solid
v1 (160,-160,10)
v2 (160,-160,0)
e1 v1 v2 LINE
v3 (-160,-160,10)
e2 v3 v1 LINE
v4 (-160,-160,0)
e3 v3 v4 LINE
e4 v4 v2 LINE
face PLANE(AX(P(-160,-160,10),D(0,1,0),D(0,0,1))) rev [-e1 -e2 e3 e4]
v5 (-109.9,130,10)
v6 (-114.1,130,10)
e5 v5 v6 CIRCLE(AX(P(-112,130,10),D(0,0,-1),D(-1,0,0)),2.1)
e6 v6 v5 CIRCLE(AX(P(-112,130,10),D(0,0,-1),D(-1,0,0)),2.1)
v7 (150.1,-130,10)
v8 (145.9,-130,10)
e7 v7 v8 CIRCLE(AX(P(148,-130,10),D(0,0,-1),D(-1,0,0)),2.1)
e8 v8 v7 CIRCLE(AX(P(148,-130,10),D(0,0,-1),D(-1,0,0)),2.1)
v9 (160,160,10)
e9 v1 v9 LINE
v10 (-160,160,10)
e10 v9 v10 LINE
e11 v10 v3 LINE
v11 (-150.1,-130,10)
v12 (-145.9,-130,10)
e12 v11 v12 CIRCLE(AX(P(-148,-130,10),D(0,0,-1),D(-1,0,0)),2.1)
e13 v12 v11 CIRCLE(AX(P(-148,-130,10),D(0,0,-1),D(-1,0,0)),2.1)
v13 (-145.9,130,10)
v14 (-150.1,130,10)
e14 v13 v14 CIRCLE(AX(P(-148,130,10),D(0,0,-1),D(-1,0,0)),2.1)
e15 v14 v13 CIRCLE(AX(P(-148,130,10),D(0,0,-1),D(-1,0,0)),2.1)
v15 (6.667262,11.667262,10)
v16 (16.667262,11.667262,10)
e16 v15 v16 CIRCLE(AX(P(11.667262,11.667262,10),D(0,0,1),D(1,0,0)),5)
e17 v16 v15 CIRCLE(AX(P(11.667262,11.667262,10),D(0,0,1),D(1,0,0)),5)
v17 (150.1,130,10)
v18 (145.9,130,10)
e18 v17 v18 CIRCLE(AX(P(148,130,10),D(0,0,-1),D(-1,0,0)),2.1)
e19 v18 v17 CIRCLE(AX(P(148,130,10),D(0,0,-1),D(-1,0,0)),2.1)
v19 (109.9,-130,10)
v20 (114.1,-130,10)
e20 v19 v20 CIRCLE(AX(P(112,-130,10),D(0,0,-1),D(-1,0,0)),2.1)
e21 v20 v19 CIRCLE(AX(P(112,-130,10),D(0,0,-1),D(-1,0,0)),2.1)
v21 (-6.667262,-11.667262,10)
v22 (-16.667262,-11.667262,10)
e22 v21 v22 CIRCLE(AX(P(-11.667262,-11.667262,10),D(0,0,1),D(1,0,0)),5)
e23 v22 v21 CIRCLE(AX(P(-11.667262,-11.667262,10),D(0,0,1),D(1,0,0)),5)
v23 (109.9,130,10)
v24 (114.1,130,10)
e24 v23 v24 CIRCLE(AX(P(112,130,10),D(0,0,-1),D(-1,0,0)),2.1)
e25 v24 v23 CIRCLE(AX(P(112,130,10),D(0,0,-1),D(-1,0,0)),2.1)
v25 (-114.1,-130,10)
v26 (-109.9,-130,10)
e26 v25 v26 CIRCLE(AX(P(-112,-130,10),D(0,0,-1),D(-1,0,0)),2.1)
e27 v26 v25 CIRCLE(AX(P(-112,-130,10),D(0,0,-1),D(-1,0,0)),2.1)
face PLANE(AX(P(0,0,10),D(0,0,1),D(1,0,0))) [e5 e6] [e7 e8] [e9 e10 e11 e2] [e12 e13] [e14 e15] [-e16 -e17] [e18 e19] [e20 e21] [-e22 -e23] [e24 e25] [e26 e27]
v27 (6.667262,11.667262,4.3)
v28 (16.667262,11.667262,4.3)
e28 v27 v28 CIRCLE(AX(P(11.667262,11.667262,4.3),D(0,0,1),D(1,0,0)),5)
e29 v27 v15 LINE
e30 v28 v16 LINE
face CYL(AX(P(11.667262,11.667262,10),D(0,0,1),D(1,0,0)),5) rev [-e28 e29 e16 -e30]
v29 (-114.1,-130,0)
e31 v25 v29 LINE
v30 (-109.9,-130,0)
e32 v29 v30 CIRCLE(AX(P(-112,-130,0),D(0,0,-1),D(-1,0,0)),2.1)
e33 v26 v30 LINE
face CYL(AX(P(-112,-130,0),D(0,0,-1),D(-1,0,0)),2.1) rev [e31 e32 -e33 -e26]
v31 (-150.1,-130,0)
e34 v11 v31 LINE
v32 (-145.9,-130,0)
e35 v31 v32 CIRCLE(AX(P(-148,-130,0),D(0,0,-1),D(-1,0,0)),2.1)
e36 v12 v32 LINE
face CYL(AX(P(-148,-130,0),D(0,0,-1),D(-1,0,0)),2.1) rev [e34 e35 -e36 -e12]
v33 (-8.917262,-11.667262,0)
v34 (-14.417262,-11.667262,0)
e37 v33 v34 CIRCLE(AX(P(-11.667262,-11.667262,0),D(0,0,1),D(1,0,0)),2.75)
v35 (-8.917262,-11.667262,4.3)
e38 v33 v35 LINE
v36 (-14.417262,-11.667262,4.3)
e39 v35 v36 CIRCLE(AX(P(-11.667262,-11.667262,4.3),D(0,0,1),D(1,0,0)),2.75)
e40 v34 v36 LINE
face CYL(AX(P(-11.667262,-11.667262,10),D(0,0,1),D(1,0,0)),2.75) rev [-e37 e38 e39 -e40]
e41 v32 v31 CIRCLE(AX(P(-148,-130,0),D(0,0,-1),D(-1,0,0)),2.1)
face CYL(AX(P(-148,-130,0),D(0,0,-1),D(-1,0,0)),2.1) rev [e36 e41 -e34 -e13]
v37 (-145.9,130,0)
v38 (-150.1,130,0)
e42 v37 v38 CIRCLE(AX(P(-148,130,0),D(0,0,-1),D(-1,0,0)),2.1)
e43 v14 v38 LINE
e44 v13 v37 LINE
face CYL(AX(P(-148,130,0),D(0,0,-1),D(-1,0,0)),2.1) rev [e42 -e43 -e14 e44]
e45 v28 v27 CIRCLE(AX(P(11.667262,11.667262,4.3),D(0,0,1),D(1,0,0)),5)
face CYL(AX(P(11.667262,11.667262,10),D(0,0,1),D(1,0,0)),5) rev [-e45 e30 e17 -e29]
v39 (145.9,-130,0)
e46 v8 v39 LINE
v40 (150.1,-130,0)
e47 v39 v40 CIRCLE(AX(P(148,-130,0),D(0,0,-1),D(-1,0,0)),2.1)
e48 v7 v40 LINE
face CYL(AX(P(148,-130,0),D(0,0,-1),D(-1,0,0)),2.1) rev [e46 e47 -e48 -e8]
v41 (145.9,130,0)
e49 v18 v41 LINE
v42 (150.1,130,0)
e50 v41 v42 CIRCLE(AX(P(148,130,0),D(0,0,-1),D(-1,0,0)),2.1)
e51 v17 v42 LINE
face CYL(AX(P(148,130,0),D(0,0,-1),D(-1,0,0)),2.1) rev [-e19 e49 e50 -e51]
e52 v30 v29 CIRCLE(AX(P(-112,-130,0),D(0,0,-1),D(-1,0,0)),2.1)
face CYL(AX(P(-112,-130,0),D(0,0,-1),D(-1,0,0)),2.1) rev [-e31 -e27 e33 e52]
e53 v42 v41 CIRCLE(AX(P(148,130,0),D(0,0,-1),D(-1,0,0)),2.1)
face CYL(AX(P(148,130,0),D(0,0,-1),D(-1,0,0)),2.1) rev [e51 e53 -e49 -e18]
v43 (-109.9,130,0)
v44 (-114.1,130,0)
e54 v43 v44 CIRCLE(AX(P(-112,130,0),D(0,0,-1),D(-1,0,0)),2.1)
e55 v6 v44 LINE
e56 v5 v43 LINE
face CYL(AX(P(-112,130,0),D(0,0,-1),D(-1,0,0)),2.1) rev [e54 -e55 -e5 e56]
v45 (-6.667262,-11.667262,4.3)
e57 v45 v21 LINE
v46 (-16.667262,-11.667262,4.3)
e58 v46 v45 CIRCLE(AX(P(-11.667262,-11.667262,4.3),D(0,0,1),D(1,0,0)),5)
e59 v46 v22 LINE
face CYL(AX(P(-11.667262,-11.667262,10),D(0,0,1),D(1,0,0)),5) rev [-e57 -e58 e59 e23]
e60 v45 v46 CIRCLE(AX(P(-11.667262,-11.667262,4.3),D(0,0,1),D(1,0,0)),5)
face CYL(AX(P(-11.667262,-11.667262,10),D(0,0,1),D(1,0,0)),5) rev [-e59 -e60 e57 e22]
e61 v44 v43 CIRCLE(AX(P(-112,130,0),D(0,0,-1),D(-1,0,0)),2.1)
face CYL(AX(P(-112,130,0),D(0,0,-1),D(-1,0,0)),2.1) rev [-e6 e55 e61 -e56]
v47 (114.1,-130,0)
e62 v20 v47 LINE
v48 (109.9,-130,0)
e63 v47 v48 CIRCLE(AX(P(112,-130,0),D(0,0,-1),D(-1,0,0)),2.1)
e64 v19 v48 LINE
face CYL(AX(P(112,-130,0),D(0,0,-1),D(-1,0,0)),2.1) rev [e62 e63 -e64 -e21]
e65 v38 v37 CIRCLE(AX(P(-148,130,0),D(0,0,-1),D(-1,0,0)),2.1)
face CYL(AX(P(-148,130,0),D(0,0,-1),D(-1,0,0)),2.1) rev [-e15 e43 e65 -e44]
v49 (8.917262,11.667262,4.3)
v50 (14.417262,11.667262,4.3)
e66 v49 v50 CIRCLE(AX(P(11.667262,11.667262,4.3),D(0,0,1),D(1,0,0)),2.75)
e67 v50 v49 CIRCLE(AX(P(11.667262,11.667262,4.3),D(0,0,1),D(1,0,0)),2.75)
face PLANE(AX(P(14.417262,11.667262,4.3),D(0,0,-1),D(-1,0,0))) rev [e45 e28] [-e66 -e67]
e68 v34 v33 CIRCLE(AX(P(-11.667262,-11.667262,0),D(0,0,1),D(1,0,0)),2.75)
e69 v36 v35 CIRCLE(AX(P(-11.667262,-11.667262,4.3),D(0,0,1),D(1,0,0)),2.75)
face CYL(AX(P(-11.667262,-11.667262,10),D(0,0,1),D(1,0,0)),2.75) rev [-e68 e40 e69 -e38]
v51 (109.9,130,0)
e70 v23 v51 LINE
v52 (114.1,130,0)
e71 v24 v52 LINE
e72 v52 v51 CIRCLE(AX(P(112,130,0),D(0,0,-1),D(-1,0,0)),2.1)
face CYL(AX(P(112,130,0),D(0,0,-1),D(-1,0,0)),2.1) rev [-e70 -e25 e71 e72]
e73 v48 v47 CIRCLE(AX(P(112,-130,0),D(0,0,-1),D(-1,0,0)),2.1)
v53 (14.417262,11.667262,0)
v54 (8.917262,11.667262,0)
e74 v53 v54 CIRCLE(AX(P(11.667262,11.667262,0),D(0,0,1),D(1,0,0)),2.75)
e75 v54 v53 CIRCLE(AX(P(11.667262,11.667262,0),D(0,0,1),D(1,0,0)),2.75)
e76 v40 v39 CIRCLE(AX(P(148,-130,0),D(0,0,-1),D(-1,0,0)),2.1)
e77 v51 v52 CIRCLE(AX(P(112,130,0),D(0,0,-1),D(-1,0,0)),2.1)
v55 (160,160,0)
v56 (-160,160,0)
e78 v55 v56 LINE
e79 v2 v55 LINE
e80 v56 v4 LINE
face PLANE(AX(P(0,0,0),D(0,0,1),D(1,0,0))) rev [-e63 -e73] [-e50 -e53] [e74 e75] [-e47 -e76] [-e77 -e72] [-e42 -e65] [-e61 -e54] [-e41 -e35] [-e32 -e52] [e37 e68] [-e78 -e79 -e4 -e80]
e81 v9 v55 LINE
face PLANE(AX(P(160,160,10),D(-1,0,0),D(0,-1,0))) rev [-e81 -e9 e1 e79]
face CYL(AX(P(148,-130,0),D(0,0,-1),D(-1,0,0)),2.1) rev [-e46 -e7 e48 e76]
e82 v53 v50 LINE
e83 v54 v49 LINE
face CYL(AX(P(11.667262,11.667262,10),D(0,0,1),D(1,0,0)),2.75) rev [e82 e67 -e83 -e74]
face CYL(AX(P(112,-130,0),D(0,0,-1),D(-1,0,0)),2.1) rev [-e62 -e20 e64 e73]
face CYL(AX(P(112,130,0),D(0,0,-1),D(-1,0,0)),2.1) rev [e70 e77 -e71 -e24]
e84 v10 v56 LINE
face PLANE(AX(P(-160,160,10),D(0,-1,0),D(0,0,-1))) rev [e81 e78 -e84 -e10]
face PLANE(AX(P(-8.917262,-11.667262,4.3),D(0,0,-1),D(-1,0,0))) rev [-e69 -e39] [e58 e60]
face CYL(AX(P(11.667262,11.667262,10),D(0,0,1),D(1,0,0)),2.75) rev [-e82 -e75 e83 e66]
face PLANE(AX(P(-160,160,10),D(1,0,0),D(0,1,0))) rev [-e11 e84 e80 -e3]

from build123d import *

# Parameters (mm, degrees)
SKETCH_1_W                = 320
SKETCH_1_H                = 320
EXTRUDE_1_DEPTH           = 10
HOLE_WIZARD_1_D           = 5.5
HOLE_WIZARD_1_DEPTH       = 10
HOLE_WIZARD_1_CBORE_D     = 10
HOLE_WIZARD_1_CBORE_DEPTH = 5.7
HOLE_WIZARD_1_TIP         = 1.652366702
HOLE_WIZARD_M5_1_D        = 4.2
MIRROR_2_COPY_1_D         = 4.2


with BuildPart() as part:
    # 草图1 → 凸台-拉伸1 (new body)
    with BuildSketch(Plane.XY):
        Rectangle(SKETCH_1_W, SKETCH_1_H)
    extrude(amount=EXTRUDE_1_DEPTH)

    # 打孔尺寸(%根据)内六角圆柱头螺钉的类型1
    with Locations(Plane.XY.offset(10)):
        with Locations((-11.66726189, -11.66726189), (11.66726189, 11.66726189)):
            CounterBoreHole(HOLE_WIZARD_1_D / 2, HOLE_WIZARD_1_CBORE_D / 2, HOLE_WIZARD_1_CBORE_DEPTH, depth=HOLE_WIZARD_1_DEPTH)
            with Locations((0, 0, -(HOLE_WIZARD_1_DEPTH + HOLE_WIZARD_1_TIP / 2))):  # 118° drill point
                Cone(0, HOLE_WIZARD_1_D / 2, HOLE_WIZARD_1_TIP, mode=Mode.SUBTRACT)

    # M5 螺纹孔1 (through all)
    with Locations(Plane(origin=(0, 0, 0), x_dir=(-1, 0, 0), z_dir=(0, 0, -1))):
        with Locations((-148, 130), (-112, 130)):
            hole_wizard_m5_1 = Hole(HOLE_WIZARD_M5_1_D / 2)

    # 镜向1: M5 螺纹孔1 across plane
    add(hole_wizard_m5_1.mirror(Plane.ZX), mode=Mode.SUBTRACT)

    # 镜向2: M5 螺纹孔1 across plane
    add(hole_wizard_m5_1.mirror(Plane(origin=(0, 0, 0), x_dir=(0, 0, 1), z_dir=(1, 0, 0))), mode=Mode.SUBTRACT)

    # 镜向2 copy 1 (through all)
    with Locations(Plane(origin=(0, 0, 0), x_dir=(1, 0, 0), z_dir=(0, 0, -1))):
        with Locations((-148, 130), (-112, 130)):
            Hole(MIRROR_2_COPY_1_D / 2)


solid = part.part
